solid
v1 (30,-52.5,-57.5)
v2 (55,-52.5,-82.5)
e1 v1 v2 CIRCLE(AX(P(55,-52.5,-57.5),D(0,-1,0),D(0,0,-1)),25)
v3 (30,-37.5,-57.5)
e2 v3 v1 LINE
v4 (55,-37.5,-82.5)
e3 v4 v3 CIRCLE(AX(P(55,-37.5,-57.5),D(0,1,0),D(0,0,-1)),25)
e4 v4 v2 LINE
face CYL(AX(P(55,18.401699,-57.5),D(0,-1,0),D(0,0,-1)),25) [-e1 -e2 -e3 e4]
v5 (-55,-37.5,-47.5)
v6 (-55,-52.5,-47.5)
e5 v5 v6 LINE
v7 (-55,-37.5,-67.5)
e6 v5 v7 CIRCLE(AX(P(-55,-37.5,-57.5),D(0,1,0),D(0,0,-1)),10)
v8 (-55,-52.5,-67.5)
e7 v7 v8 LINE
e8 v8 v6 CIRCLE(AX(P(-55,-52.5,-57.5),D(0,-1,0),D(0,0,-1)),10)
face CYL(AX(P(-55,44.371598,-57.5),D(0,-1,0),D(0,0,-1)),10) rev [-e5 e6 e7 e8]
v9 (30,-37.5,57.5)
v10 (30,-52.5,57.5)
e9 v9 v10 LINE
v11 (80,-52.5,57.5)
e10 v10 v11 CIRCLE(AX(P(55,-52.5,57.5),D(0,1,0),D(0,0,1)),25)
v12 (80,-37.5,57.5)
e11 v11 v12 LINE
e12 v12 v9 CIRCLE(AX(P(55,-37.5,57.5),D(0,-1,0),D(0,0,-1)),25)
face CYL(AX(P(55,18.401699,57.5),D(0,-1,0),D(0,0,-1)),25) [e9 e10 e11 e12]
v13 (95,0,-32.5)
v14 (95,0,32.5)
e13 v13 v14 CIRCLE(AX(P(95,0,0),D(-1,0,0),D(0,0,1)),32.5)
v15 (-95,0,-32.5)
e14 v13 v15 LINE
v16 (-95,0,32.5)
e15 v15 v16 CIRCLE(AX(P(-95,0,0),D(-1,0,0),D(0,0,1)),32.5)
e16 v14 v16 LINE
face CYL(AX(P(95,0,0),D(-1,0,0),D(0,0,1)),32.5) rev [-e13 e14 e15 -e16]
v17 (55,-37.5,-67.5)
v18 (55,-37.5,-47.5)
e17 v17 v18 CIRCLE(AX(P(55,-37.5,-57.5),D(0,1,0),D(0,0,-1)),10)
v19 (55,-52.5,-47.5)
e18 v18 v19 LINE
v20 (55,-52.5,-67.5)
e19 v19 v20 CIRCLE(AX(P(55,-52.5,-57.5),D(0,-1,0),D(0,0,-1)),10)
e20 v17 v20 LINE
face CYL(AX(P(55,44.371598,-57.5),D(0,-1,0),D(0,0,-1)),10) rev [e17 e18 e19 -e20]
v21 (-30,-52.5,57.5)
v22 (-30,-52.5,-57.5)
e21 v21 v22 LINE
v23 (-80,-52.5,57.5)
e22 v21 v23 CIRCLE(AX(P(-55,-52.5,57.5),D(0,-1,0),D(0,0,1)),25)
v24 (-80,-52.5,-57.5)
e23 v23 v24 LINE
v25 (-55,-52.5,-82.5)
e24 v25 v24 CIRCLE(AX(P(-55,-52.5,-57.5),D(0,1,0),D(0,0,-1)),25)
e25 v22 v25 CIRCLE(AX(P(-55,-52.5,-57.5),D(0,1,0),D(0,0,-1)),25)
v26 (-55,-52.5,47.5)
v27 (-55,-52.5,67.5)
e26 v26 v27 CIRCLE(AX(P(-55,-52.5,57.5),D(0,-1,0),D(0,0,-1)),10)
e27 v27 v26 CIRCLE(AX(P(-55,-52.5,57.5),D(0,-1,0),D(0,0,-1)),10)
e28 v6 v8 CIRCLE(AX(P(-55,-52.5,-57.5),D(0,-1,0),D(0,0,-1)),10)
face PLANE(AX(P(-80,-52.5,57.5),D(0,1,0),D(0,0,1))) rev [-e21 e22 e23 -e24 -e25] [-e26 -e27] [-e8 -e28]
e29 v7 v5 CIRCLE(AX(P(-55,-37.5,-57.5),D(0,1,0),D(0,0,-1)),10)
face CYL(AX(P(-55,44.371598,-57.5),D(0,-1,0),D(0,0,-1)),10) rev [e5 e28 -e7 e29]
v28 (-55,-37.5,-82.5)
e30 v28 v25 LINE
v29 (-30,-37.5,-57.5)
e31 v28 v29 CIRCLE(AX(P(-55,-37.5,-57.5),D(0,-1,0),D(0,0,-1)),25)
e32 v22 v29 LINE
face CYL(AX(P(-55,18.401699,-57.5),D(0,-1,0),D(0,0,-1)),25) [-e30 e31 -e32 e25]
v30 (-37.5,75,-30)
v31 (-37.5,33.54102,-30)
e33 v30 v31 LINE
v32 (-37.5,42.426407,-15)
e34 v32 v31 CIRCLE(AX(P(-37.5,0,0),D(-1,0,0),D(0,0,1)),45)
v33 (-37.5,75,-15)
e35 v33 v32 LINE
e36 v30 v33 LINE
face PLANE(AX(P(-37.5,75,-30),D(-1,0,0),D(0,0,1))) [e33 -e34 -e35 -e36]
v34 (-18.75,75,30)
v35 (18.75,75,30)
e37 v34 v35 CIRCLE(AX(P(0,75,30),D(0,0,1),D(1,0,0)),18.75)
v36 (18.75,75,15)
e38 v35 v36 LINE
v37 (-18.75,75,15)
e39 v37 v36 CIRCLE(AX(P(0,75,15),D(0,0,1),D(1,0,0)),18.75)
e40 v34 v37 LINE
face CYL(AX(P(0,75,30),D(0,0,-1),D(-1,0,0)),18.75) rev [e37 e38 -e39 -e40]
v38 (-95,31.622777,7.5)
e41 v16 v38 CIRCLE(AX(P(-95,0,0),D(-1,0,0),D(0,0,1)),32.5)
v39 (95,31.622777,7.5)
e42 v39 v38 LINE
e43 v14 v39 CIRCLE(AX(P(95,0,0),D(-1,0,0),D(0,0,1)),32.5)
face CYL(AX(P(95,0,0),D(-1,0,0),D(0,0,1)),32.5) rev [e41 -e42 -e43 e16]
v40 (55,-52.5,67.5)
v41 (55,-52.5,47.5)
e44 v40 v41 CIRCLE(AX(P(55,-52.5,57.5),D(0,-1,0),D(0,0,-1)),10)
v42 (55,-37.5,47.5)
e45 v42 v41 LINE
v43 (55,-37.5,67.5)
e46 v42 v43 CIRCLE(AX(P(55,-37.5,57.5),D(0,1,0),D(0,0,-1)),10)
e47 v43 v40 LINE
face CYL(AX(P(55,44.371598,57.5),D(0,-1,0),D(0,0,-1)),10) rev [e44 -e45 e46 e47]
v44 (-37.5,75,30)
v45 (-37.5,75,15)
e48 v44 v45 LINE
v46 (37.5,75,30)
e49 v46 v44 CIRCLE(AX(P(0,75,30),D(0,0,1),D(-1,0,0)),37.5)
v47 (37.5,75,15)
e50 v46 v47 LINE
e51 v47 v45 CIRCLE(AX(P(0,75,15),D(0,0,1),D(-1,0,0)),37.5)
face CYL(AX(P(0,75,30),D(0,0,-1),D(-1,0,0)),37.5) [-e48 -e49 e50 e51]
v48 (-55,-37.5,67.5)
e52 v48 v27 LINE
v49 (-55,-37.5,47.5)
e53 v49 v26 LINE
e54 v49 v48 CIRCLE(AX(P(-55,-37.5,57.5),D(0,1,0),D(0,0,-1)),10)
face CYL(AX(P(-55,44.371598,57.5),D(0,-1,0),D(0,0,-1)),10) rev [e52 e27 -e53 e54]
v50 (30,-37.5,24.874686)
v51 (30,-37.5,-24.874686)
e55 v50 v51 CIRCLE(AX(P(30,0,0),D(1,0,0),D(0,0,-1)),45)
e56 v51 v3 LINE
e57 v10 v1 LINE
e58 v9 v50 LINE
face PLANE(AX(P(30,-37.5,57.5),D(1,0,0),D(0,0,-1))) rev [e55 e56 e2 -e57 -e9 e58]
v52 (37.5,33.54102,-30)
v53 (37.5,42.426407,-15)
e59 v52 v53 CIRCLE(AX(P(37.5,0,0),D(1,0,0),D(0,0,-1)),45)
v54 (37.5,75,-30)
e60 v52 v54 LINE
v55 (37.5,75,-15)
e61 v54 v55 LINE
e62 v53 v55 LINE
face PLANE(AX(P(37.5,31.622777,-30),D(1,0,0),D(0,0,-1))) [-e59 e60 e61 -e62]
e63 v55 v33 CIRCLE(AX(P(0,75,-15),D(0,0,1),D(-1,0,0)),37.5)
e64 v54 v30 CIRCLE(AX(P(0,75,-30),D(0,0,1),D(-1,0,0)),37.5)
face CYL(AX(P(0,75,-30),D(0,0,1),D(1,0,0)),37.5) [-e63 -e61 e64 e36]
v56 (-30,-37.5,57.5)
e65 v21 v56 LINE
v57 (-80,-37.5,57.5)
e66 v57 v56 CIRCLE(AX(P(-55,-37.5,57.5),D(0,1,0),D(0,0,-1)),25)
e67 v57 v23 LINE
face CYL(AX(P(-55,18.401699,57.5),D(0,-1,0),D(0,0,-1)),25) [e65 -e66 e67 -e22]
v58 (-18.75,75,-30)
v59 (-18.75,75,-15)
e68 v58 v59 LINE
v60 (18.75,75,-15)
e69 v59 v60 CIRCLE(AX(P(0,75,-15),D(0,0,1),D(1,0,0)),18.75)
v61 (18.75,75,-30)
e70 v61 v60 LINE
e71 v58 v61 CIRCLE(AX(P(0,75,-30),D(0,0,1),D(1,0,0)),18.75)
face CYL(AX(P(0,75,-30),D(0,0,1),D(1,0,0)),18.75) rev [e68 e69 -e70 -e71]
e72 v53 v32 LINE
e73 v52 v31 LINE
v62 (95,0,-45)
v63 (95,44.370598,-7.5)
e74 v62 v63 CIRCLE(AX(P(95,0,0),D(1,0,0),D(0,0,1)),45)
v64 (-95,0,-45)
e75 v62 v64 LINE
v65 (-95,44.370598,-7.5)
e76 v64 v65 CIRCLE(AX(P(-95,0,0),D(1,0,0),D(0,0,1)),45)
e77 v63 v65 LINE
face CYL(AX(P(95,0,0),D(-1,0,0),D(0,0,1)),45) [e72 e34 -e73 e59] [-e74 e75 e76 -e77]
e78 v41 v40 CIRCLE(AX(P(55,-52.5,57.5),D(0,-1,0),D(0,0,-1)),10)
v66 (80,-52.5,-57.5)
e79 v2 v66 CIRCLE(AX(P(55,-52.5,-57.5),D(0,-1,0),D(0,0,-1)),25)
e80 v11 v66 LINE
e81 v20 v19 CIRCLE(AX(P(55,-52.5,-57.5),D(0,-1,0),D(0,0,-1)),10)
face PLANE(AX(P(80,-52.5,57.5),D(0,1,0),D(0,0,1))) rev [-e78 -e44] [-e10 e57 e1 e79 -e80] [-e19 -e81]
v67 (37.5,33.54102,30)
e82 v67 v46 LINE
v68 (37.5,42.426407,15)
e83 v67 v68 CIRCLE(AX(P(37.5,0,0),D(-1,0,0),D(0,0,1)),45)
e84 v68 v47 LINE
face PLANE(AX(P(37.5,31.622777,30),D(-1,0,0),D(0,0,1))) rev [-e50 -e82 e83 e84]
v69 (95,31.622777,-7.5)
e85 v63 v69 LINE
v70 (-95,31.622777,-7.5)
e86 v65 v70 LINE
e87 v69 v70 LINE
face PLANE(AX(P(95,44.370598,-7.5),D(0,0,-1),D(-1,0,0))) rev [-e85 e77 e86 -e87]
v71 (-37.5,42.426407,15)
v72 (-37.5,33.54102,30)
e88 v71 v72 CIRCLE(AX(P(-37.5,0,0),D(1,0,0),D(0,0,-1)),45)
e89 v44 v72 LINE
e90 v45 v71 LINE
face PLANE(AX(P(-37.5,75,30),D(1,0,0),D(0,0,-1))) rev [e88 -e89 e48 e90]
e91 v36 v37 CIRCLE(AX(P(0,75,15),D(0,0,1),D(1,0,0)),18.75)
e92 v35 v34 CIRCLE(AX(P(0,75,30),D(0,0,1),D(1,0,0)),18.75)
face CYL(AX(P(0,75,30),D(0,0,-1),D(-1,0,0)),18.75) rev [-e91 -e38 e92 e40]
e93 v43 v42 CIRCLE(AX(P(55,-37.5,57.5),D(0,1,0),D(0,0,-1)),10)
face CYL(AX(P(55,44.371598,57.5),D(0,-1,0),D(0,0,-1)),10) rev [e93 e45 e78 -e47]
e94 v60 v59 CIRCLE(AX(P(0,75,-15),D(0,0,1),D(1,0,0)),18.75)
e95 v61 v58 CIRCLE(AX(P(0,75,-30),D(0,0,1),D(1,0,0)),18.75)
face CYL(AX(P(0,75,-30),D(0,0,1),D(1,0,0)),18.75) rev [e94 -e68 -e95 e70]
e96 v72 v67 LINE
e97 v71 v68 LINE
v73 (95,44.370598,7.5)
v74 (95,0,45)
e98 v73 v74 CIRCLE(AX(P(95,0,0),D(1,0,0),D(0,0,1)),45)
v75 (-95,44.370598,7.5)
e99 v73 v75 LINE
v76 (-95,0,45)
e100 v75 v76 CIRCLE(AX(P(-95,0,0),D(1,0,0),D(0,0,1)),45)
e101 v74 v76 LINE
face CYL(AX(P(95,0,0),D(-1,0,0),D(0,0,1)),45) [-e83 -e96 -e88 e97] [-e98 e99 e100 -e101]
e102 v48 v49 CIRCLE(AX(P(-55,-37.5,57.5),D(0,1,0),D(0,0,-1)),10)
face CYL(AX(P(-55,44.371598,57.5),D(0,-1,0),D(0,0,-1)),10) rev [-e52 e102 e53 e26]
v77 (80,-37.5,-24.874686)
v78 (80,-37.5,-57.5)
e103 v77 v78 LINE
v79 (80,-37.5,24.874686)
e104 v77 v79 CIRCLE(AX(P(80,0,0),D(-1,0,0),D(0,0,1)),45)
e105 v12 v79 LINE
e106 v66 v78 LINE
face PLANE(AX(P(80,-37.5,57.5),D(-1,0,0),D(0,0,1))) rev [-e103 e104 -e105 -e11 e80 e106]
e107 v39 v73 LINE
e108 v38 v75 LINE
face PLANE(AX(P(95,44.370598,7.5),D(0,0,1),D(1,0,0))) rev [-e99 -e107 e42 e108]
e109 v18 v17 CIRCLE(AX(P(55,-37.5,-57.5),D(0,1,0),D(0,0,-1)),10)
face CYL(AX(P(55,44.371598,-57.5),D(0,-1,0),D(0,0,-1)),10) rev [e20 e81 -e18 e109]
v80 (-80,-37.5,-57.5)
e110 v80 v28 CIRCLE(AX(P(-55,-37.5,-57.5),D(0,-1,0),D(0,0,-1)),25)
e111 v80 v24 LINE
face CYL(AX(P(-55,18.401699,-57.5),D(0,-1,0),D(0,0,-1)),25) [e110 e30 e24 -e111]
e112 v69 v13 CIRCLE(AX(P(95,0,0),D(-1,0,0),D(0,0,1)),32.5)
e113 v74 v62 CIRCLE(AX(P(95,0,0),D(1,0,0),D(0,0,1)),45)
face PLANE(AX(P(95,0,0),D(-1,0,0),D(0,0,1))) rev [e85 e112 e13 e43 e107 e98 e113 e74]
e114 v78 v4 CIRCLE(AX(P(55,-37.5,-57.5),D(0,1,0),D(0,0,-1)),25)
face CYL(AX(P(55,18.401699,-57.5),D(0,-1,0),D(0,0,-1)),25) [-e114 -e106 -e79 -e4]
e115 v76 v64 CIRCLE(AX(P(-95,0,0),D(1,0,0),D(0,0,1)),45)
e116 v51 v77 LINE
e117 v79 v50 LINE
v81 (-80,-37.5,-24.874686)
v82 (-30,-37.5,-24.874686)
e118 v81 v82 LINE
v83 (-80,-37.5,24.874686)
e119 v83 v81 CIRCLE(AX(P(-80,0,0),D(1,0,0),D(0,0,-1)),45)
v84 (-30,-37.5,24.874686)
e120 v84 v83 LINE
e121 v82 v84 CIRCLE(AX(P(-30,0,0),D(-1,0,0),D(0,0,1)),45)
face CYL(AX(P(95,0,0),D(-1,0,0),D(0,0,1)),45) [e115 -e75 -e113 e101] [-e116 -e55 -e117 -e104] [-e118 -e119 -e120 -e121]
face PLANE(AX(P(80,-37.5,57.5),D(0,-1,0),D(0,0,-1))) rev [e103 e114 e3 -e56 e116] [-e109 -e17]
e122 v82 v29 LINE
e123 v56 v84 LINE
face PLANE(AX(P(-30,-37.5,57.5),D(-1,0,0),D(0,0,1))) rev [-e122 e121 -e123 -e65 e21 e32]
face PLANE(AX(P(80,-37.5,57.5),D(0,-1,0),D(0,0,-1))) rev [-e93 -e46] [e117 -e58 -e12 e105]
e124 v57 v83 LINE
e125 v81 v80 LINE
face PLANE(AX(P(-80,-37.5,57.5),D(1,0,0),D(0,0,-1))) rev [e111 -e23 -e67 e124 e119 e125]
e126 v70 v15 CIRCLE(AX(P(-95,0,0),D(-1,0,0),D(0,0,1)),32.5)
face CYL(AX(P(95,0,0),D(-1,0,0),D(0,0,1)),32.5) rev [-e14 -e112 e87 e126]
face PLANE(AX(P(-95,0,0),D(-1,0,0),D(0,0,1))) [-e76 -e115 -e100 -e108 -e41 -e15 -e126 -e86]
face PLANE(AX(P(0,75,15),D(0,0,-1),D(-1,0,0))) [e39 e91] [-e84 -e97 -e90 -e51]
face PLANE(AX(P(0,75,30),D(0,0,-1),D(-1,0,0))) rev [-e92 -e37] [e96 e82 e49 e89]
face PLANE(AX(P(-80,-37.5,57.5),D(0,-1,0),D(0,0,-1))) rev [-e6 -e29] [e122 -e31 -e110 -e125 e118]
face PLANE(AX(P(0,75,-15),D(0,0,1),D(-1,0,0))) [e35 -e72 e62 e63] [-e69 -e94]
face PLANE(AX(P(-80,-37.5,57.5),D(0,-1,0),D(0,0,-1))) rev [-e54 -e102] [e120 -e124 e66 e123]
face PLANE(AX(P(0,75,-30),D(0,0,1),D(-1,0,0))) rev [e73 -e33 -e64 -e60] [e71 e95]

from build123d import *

# Parameters (mm, degrees)
SPLIT_SLEEVE_DEPTH                 = 95
SADDLE_BASE_PROFILE_W              = 50
SADDLE_BASE_PROFILE_H              = 15
SADDLE_BASE_DEPTH                  = 57.5
FOOT_TAB_DEPTH                     = 15
FOOT_TAB_MIRROR_RIGHT_COPY_1_DEPTH = 15
FOOT_MOUNTING_HOLES_4X_REACH       = 160.793
FOOT_HOLE_PROFILE_R                = 10
CLAMP_LUG_PROFILE_R                = 18.75
CLAMP_LUG_DEPTH                    = 15


with BuildPart() as part:
    # Split Sleeve Profile → Split Sleeve (new, symmetric)
    with BuildSketch(Plane(origin=(0, 0, 0), x_dir=(0, 0, -1), z_dir=(1, 0, 0))):
        with BuildLine():
            Line((-7.5, 44.370598373), (-7.5, 31.622776602))
            ThreePointArc((-7.5, 31.622776602), (0, -32.5), (7.5, 31.622776602))
            Line((7.5, 31.622776602), (7.5, 44.370598373))
            ThreePointArc((7.5, 44.370598373), (0, -45), (-7.5, 44.370598373))
        make_face()
    extrude(amount=SPLIT_SLEEVE_DEPTH, both=True)

    # Saddle Base Profile → Saddle Base (add, symmetric)
    with BuildSketch(Plane.XY):
        with Locations((-55, -45)):
            Rectangle(SADDLE_BASE_PROFILE_W, SADDLE_BASE_PROFILE_H)
        with Locations((55, -45)):
            Rectangle(SADDLE_BASE_PROFILE_W, SADDLE_BASE_PROFILE_H)
    extrude(amount=SADDLE_BASE_DEPTH, both=True)

    # Foot Tab Profile → Foot Tab (add)
    with BuildSketch(Plane.XZ.offset(52.5)):
        with BuildLine():
            Line((-80, 57.5), (-30, 57.5))
            ThreePointArc((-30, 57.5), (-55, 82.5), (-80, 57.5))
        make_face()
    foot_tab = extrude(amount=-FOOT_TAB_DEPTH)

    # Foot Tab Mirror Front: Foot Tab across plane
    add(foot_tab.mirror(Plane.XY))

    # Foot Tab Mirror Right: Foot Tab across plane
    add(foot_tab.mirror(Plane(origin=(0, 0, 0), x_dir=(0, 0, 1), z_dir=(1, 0, 0))))

    # Foot Tab Mirror Right copy 1 sketch → Foot Tab Mirror Right copy 1 (add)
    with BuildSketch(Plane(origin=(0, -52.5, 0), x_dir=(-1, 0, 0), z_dir=(0, -1, 0))):
        with BuildLine():
            Line((-80, 57.5), (-30, 57.5))
            ThreePointArc((-30, 57.5), (-55, 82.5), (-80, 57.5))
        make_face()
    extrude(amount=-FOOT_TAB_MIRROR_RIGHT_COPY_1_DEPTH)

    # Foot Hole Profile → Foot Mounting Holes 4x (cut, up to next)
    with BuildSketch(Plane.XZ.offset(52.5), mode=Mode.PRIVATE) as foot_mounting_holes_4x_sk1:
        with Locations(Location((-55, 57.5, 0), (0, 0, 270))):
            Circle(FOOT_HOLE_PROFILE_R)
    foot_mounting_holes_4x_tool1 = extrude(foot_mounting_holes_4x_sk1.sketch, amount=-FOOT_MOUNTING_HOLES_4X_REACH, mode=Mode.PRIVATE) & part.part
    # Foot Hole Profile → Foot Mounting Holes 4x (cut, up to next)
    with BuildSketch(Plane.XZ.offset(52.5), mode=Mode.PRIVATE) as foot_mounting_holes_4x_sk2:
        with Locations(Location((-55, -57.5, 0), (0, 0, 270))):
            Circle(FOOT_HOLE_PROFILE_R)
    foot_mounting_holes_4x_tool2 = extrude(foot_mounting_holes_4x_sk2.sketch, amount=-FOOT_MOUNTING_HOLES_4X_REACH, mode=Mode.PRIVATE) & part.part
    # Foot Hole Profile → Foot Mounting Holes 4x (cut, up to next)
    with BuildSketch(Plane.XZ.offset(52.5), mode=Mode.PRIVATE) as foot_mounting_holes_4x_sk3:
        with Locations(Location((55, -57.5, 0), (0, 0, 270))):
            Circle(FOOT_HOLE_PROFILE_R)
    foot_mounting_holes_4x_tool3 = extrude(foot_mounting_holes_4x_sk3.sketch, amount=-FOOT_MOUNTING_HOLES_4X_REACH, mode=Mode.PRIVATE) & part.part
    # Foot Hole Profile → Foot Mounting Holes 4x (cut, up to next)
    with BuildSketch(Plane.XZ.offset(52.5), mode=Mode.PRIVATE) as foot_mounting_holes_4x_sk4:
        with Locations(Location((55, 57.5, 0), (0, 0, 270))):
            Circle(FOOT_HOLE_PROFILE_R)
    foot_mounting_holes_4x_tool4 = extrude(foot_mounting_holes_4x_sk4.sketch, amount=-FOOT_MOUNTING_HOLES_4X_REACH, mode=Mode.PRIVATE) & part.part
    add(foot_mounting_holes_4x_tool1.solids().sort_by_distance((-55, -52.5, 57.5))[0], mode=Mode.SUBTRACT)
    add(foot_mounting_holes_4x_tool2.solids().sort_by_distance((-55, -52.5, -57.5))[0], mode=Mode.SUBTRACT)
    add(foot_mounting_holes_4x_tool3.solids().sort_by_distance((55, -52.5, -57.5))[0], mode=Mode.SUBTRACT)
    add(foot_mounting_holes_4x_tool4.solids().sort_by_distance((55, -52.5, 57.5))[0], mode=Mode.SUBTRACT)

    # Clamp Lug Profile → Clamp Lug (add)
    with BuildSketch(Plane.XY.offset(15)):
        with BuildLine():
            Line((-37.5, 75), (-37.5, 31.622776602))
            Line((-37.5, 31.622776602), (37.5, 31.622776602))
            Line((37.5, 31.622776602), (37.5, 75))
            ThreePointArc((37.5, 75), (0, 112.5), (-37.5, 75))
        make_face()
        with Locations((0, 75)):
            Circle(CLAMP_LUG_PROFILE_R, mode=Mode.SUBTRACT)
    clamp_lug = extrude(amount=CLAMP_LUG_DEPTH)

    # Clamp Lug Mirror: Clamp Lug across plane
    add(clamp_lug.mirror(Plane.XY))


solid = part.part
